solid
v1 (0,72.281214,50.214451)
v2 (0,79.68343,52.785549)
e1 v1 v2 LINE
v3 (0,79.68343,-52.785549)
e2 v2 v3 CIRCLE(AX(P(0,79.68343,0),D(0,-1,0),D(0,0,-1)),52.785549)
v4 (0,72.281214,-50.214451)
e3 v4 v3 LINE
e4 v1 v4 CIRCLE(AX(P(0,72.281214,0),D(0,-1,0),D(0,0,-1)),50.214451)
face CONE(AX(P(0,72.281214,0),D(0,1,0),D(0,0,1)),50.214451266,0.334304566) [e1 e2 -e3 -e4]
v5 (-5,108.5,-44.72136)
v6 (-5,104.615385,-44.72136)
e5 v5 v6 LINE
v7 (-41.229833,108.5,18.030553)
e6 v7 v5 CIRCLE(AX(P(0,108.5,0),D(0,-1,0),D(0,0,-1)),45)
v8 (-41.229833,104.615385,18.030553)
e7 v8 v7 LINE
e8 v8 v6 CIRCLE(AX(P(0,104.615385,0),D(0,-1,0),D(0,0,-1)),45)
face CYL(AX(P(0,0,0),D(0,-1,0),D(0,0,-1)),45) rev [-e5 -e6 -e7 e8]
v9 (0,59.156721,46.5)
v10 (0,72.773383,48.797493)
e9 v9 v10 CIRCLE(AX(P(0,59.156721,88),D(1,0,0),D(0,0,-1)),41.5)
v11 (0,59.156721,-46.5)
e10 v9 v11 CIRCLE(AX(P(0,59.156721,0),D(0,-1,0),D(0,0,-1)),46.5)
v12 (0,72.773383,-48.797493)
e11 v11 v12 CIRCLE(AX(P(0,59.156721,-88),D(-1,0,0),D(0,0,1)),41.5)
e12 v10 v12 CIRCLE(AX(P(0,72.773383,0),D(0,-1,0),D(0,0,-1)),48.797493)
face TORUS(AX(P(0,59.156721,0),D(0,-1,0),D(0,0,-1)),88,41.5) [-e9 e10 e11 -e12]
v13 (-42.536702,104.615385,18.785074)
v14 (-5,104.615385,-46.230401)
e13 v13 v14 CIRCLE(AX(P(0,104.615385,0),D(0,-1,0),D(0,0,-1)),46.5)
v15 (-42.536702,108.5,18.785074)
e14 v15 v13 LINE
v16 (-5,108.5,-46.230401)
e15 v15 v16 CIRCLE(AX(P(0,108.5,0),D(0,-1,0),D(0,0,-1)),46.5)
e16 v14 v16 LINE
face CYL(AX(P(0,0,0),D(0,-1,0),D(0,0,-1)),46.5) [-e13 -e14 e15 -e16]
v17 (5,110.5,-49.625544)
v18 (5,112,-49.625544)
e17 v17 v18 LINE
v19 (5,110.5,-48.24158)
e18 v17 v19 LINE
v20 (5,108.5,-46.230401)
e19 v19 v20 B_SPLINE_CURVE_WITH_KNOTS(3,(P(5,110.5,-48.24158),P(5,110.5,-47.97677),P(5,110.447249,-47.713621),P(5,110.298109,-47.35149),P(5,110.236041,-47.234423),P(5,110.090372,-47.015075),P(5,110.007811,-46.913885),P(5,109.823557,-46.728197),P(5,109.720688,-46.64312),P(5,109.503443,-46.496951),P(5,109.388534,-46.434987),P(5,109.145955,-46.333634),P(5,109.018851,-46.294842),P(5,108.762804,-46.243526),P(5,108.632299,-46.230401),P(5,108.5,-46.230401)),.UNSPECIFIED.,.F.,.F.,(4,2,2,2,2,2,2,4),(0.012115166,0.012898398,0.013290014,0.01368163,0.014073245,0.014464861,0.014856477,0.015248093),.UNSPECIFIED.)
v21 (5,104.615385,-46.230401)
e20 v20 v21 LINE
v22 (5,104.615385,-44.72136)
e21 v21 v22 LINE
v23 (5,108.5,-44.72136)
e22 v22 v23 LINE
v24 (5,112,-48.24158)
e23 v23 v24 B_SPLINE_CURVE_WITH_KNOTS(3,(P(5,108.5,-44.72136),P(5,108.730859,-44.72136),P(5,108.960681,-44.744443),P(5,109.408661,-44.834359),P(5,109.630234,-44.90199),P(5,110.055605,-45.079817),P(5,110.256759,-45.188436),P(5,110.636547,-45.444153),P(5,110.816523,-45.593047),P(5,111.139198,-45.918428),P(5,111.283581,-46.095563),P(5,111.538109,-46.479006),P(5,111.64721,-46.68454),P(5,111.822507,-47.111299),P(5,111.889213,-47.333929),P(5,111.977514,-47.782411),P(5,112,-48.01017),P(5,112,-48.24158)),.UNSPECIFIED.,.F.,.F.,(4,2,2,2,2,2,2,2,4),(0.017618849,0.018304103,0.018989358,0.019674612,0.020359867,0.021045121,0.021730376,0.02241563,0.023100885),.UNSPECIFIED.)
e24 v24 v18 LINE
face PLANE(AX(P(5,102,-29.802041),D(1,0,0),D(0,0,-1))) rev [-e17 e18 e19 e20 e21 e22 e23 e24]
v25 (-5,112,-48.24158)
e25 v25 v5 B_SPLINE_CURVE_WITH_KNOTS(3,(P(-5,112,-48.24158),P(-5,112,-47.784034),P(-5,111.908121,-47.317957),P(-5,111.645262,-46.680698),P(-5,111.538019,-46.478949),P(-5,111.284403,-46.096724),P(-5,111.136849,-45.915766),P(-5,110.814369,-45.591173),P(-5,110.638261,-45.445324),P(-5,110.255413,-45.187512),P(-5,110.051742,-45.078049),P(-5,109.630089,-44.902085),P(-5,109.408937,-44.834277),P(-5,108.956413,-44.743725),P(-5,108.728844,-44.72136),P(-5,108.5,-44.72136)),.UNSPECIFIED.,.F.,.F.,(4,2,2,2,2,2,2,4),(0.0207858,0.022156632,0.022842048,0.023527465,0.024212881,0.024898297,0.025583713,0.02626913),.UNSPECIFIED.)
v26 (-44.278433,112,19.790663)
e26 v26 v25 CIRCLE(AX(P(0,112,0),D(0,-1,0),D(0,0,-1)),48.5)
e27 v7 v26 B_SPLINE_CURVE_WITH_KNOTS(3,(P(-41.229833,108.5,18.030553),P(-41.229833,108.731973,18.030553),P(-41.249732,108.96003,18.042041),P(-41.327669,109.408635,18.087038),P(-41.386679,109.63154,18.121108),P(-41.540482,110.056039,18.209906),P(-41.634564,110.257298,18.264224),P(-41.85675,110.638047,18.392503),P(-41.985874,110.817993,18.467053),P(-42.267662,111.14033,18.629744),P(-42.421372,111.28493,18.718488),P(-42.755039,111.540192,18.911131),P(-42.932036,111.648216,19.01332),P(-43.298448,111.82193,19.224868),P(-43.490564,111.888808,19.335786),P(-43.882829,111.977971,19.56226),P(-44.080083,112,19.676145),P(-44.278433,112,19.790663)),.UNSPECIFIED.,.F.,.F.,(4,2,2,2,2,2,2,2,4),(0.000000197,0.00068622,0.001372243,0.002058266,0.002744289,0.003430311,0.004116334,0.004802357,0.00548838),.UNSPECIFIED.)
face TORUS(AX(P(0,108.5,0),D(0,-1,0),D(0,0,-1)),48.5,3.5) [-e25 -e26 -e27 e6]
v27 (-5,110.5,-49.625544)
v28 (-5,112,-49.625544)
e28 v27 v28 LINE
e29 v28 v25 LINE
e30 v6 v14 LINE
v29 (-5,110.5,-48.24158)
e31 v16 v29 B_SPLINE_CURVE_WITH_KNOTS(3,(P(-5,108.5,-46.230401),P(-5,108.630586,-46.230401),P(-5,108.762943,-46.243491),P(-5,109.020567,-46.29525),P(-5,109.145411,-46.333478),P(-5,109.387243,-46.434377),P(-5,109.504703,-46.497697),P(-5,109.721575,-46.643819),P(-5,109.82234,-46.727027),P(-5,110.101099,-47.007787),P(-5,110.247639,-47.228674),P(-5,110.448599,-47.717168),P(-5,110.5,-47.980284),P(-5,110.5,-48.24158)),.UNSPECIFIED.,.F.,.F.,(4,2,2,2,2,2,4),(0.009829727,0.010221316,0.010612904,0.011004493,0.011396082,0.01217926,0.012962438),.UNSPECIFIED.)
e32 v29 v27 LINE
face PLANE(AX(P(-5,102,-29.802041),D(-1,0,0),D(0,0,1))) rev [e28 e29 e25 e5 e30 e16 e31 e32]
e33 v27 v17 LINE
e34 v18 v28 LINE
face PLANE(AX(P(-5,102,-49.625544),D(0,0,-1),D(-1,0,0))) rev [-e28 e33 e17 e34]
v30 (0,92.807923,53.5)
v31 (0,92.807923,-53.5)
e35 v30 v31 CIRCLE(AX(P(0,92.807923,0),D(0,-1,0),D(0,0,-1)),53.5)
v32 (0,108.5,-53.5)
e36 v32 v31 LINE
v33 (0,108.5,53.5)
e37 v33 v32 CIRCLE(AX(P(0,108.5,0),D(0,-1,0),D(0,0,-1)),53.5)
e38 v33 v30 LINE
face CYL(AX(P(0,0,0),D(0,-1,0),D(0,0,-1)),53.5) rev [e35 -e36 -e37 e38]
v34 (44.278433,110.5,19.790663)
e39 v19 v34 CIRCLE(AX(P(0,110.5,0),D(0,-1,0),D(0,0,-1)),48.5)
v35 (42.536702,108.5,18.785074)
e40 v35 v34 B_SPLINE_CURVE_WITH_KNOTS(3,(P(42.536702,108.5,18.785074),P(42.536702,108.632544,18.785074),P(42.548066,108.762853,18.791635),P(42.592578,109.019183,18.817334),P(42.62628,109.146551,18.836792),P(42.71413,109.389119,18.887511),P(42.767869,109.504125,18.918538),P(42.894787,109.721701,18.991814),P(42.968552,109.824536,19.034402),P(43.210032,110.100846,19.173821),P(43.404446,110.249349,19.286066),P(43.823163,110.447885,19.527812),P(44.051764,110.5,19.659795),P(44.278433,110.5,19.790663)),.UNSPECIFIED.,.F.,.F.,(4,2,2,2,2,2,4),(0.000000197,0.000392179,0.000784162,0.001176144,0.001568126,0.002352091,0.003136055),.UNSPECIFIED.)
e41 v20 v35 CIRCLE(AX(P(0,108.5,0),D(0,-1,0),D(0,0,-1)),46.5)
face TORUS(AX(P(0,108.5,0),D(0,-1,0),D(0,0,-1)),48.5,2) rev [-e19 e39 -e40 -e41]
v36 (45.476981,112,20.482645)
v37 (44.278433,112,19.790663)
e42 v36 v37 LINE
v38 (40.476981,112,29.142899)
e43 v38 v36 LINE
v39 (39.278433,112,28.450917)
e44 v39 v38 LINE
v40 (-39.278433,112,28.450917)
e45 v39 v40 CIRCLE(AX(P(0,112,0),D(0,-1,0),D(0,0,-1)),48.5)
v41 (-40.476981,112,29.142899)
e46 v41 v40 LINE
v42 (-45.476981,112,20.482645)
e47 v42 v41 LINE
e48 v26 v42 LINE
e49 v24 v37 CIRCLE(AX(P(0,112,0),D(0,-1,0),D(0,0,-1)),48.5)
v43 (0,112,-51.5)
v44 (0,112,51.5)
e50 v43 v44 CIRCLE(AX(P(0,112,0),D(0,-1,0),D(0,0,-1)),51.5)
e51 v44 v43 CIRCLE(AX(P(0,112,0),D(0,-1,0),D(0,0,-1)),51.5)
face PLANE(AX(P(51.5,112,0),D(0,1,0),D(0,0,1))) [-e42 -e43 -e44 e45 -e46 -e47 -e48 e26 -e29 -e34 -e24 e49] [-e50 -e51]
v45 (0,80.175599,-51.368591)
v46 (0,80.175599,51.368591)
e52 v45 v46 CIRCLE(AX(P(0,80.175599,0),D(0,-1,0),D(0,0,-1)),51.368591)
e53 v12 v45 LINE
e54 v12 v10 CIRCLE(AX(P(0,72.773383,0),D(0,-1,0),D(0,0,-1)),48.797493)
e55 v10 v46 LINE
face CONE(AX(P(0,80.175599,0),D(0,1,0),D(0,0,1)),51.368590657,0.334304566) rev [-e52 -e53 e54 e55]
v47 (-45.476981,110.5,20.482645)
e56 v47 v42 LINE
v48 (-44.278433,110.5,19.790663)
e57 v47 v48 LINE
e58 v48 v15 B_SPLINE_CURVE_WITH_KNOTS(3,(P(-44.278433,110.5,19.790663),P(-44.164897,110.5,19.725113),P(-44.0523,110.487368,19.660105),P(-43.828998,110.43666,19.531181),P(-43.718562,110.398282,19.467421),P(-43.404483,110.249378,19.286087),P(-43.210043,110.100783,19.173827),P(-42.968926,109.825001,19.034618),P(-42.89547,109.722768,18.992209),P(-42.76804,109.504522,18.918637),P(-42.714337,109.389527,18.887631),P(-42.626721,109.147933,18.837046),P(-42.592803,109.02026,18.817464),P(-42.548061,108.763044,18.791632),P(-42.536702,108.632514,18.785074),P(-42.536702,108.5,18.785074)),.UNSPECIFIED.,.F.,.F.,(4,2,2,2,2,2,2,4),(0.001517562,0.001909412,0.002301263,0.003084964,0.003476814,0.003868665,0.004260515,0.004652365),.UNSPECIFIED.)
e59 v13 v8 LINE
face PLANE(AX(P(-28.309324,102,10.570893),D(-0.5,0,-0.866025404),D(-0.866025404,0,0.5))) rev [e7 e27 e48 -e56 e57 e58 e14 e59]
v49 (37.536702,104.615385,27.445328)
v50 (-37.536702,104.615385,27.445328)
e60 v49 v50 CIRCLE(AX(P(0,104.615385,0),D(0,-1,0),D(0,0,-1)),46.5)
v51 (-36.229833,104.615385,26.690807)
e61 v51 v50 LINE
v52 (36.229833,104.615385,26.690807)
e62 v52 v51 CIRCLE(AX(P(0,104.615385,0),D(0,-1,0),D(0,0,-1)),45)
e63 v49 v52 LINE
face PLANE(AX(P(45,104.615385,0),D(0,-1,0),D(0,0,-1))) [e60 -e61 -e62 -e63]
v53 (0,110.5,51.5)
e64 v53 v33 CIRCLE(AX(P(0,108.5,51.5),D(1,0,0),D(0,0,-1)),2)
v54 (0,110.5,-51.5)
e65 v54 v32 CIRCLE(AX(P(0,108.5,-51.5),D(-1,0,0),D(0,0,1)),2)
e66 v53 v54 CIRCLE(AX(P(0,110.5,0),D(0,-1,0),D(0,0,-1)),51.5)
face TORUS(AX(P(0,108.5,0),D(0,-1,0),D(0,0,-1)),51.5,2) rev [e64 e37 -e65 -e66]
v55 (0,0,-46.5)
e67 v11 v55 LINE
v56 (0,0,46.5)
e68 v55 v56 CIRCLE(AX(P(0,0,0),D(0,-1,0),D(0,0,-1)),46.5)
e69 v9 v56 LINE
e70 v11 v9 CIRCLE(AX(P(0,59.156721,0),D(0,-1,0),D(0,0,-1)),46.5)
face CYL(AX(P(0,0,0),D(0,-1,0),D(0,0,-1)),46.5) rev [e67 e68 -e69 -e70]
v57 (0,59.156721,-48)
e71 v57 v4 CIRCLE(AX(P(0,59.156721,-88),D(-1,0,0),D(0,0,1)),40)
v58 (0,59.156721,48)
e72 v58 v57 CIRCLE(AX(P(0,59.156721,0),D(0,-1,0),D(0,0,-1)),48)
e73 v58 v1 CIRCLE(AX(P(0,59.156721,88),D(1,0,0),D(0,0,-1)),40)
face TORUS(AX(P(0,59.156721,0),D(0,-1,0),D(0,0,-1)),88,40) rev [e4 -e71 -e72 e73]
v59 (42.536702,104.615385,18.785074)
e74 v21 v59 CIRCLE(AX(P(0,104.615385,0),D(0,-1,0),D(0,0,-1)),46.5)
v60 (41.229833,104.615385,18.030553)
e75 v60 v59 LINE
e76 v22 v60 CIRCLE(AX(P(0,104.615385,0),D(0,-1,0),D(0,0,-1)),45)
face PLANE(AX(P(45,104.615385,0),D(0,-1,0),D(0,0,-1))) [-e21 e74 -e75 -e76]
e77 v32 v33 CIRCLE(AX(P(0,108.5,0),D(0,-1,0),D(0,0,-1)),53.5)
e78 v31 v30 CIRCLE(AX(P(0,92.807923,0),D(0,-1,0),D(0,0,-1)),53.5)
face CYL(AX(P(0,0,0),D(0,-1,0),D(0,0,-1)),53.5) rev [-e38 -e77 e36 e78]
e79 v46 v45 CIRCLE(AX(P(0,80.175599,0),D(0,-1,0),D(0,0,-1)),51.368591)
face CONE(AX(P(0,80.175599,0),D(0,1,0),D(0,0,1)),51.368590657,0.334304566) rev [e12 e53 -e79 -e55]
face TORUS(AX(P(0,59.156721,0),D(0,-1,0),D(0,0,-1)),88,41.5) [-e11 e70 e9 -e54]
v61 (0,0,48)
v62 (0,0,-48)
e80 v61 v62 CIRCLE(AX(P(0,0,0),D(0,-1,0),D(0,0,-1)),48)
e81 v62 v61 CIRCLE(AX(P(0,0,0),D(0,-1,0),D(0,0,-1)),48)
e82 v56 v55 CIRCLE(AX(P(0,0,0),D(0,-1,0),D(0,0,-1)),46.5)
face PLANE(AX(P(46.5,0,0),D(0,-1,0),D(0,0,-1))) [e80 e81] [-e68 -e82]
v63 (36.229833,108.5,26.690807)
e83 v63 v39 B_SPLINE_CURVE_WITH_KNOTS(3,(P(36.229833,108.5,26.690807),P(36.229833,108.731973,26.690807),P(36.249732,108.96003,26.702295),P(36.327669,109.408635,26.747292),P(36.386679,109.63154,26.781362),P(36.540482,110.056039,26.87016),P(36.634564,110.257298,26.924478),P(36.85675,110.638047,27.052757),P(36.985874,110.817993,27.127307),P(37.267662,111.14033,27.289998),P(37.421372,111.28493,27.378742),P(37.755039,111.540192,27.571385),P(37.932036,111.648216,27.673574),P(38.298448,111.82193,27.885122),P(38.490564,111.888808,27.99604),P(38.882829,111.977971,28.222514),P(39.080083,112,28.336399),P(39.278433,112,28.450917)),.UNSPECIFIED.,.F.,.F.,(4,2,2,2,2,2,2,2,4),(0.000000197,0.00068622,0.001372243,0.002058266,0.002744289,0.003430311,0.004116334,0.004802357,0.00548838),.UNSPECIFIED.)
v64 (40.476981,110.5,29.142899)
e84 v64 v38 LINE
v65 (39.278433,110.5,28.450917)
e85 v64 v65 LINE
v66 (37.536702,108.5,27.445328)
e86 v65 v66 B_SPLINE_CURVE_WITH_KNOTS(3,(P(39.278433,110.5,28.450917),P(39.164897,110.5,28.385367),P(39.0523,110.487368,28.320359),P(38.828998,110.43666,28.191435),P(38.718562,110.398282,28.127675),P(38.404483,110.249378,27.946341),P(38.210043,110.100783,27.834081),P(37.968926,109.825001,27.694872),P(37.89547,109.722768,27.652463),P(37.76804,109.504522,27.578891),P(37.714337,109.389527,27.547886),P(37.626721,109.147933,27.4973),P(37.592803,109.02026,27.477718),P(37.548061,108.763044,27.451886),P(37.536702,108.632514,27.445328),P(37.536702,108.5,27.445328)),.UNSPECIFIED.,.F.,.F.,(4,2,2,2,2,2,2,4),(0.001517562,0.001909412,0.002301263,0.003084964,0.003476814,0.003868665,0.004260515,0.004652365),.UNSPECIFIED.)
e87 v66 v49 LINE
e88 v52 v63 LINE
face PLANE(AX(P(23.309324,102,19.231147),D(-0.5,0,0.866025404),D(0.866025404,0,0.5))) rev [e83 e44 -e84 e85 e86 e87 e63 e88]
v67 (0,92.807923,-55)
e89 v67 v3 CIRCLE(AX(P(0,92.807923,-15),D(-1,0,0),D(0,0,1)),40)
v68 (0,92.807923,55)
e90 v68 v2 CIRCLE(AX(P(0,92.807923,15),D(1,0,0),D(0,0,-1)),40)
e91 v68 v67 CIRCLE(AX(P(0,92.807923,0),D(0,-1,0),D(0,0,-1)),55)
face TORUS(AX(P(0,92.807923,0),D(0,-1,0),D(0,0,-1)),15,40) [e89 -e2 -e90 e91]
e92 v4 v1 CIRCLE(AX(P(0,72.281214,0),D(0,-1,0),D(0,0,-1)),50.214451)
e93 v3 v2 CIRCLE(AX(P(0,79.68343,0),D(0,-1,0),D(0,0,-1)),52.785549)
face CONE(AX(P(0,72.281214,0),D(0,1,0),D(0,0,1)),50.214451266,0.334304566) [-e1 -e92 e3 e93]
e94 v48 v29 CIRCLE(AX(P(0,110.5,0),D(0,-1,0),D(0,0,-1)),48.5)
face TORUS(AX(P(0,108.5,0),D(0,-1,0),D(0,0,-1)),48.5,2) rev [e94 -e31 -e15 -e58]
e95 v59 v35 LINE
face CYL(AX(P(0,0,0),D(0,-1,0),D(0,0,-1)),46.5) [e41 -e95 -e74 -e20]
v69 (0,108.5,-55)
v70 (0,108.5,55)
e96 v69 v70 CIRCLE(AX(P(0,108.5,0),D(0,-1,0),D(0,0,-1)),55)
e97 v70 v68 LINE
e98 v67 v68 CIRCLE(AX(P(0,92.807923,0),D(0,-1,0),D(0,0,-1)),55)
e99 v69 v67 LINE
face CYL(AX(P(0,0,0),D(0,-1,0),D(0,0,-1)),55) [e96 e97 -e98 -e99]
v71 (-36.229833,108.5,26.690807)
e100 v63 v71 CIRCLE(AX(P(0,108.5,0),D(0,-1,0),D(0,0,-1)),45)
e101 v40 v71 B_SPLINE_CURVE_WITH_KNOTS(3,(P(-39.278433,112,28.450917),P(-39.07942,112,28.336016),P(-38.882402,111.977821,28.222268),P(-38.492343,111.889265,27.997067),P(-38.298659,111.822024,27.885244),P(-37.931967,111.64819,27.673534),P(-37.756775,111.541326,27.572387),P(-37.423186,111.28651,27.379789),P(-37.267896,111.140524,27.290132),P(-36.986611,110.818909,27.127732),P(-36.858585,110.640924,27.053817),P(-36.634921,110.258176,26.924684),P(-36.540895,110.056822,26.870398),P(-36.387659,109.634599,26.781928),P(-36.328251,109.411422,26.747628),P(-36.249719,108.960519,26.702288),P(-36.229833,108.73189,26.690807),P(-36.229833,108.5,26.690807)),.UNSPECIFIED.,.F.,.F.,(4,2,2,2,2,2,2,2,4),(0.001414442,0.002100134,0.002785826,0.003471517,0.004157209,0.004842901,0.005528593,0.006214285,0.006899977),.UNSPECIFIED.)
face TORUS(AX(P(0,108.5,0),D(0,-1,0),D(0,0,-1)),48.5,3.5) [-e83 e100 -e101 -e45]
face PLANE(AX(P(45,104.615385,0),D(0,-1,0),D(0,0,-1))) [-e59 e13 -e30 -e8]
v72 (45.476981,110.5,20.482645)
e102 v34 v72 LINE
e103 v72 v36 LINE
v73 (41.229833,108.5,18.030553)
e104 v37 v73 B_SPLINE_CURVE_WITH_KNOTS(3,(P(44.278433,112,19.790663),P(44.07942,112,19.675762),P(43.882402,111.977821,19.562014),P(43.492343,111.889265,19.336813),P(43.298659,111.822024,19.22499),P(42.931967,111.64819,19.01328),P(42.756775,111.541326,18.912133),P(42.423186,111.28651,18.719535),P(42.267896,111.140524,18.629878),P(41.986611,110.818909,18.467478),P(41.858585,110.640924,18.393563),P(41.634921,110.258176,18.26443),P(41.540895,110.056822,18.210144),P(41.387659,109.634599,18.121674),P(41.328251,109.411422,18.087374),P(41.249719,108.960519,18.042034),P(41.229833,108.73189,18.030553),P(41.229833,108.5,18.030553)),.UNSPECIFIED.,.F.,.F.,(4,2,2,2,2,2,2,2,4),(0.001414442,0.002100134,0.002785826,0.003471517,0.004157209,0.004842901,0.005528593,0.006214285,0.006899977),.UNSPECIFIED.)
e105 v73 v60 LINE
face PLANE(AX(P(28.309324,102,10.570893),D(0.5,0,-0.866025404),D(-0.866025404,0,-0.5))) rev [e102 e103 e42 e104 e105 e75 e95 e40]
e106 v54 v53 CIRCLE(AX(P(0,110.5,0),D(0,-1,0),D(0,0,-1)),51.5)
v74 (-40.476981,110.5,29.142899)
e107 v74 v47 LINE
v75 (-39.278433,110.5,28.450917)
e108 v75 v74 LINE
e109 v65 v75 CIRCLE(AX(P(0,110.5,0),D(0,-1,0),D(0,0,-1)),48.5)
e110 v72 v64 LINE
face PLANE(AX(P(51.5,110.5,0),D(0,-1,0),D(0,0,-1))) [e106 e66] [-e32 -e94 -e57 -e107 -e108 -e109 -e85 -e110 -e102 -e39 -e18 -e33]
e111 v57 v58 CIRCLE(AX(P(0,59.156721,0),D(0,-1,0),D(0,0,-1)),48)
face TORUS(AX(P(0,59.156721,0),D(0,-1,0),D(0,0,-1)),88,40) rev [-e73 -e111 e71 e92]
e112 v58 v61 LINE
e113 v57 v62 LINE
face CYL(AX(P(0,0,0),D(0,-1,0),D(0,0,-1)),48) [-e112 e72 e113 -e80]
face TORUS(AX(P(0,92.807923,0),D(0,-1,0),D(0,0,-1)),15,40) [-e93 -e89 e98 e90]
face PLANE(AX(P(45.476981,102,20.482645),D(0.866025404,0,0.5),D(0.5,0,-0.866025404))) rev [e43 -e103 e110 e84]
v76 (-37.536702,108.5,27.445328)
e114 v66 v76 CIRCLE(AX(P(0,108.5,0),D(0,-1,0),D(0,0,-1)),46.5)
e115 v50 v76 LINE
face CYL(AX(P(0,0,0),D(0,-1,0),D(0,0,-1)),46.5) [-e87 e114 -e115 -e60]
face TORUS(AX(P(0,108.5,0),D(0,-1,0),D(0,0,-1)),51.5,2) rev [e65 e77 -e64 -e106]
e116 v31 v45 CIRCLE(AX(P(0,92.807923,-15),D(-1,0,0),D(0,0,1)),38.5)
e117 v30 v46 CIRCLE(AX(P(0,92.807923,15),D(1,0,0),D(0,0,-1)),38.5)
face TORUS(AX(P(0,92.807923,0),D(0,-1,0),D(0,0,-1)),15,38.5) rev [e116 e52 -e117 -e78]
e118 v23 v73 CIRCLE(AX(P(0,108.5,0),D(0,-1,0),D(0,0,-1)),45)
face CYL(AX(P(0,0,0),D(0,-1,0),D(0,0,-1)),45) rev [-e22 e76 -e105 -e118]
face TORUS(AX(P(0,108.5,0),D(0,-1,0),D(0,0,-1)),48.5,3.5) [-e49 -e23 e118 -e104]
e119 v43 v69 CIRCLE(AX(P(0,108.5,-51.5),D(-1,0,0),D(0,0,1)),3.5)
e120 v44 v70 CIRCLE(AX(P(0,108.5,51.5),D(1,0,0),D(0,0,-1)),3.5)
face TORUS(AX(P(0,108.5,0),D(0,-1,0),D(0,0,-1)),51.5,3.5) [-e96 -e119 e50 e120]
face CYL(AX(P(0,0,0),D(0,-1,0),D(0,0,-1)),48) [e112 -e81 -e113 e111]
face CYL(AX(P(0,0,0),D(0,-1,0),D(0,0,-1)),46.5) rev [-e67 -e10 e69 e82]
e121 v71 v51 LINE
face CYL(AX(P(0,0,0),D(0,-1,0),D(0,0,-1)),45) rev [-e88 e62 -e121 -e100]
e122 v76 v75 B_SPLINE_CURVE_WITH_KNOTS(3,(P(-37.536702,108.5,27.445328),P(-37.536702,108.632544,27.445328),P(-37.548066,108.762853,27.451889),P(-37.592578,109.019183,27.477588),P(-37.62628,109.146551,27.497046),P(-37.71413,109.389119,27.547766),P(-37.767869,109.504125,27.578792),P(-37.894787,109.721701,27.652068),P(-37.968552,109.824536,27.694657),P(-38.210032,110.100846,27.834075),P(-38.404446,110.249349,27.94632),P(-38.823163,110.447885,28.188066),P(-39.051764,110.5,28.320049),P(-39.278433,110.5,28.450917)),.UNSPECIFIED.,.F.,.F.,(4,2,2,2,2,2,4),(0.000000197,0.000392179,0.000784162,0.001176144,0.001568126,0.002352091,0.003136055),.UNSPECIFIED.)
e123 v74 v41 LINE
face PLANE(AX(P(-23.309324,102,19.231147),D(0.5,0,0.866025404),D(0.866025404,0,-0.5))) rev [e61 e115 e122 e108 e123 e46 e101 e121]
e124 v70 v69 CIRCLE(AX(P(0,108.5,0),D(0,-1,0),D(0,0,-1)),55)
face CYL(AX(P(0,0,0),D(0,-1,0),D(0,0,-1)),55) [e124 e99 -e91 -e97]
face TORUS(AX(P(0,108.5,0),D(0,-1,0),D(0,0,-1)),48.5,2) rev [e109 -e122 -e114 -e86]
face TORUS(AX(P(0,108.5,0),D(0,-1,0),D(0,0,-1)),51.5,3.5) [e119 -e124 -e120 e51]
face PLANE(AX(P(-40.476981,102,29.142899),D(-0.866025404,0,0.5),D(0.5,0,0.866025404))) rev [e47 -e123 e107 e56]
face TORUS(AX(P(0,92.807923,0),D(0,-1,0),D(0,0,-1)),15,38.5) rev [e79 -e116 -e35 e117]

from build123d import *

# Parameters (mm, degrees)
SKETCH2_W          = 10
SKETCH2_H          = 19.823502967
CUT_EXTRUDE1_DEPTH = 10
CIRPATTERN1_COUNT  = 3


with BuildPart() as part:
    # Sketch1 → Revolve1 (revolve)
    with BuildSketch(Plane.XY, mode=Mode.PRIVATE) as revolve1_sk:
        with BuildLine():
            Line((48, 0), (48, 59.156721496))
            ThreePointArc((48, 59.156721496), (48.557497865, 65.81172152), (50.214451266, 72.281214129))
            Line((50.214451266, 72.281214129), (52.785548734, 79.683430077))
            ThreePointArc((52.785548734, 79.683430077), (54.442502135, 86.152922686), (55, 92.80792271))
            Line((55, 92.80792271), (55, 108.5))
            ThreePointArc((55, 108.5), (53.974873734, 110.974873734), (51.5, 112))
            Line((51.5, 112), (48.5, 112))
            ThreePointArc((48.5, 112), (46.025126266, 110.974873734), (45, 108.5))
            Line((45, 108.5), (45, 104.615384615))
            Line((45, 104.615384615), (46.5, 104.615384615))
            Line((46.5, 104.615384615), (46.5, 108.5))
            ThreePointArc((46.5, 108.5), (47.085786438, 109.914213562), (48.5, 110.5))
            Line((48.5, 110.5), (51.5, 110.5))
            ThreePointArc((51.5, 110.5), (52.914213562, 109.914213562), (53.5, 108.5))
            Line((53.5, 108.5), (53.5, 92.80792271))
            ThreePointArc((53.5, 92.80792271), (52.963408305, 86.402485187), (51.368590657, 80.175598551))
            Line((51.368590657, 80.175598551), (48.797493188, 72.773382602))
            ThreePointArc((48.797493188, 72.773382602), (47.078404035, 66.061284021), (46.5, 59.156721496))
            Line((46.5, 59.156721496), (46.5, 0))
            Line((46.5, 0), (48, 0))
        make_face()
    revolve(revolve1_sk.sketch.rotate(Axis((0, 0, 0), (0, 1, 0)), 90), axis=Axis((0, 0, 0), (0, 1, 0)))

    # Sketch2 → Cut-Extrude1 (cut)
    with BuildSketch(Plane(origin=(0, 112, 0), x_dir=(1, 0, 0), z_dir=(0, 1, 0))):
        with Locations((0, 39.713792094)):
            Rectangle(SKETCH2_W, SKETCH2_H)
    cut_extrude1 = extrude(amount=-CUT_EXTRUDE1_DEPTH, mode=Mode.SUBTRACT)

    # CirPattern1: Cut-Extrude1 ×3 about axis
    cirpattern1_axis = Axis((0, 0, 0), (0, 1, 0))
    for i in range(1, CIRPATTERN1_COUNT):
        add(cut_extrude1.rotate(cirpattern1_axis, i * 360 / CIRPATTERN1_COUNT), mode=Mode.SUBTRACT)


solid = part.part
